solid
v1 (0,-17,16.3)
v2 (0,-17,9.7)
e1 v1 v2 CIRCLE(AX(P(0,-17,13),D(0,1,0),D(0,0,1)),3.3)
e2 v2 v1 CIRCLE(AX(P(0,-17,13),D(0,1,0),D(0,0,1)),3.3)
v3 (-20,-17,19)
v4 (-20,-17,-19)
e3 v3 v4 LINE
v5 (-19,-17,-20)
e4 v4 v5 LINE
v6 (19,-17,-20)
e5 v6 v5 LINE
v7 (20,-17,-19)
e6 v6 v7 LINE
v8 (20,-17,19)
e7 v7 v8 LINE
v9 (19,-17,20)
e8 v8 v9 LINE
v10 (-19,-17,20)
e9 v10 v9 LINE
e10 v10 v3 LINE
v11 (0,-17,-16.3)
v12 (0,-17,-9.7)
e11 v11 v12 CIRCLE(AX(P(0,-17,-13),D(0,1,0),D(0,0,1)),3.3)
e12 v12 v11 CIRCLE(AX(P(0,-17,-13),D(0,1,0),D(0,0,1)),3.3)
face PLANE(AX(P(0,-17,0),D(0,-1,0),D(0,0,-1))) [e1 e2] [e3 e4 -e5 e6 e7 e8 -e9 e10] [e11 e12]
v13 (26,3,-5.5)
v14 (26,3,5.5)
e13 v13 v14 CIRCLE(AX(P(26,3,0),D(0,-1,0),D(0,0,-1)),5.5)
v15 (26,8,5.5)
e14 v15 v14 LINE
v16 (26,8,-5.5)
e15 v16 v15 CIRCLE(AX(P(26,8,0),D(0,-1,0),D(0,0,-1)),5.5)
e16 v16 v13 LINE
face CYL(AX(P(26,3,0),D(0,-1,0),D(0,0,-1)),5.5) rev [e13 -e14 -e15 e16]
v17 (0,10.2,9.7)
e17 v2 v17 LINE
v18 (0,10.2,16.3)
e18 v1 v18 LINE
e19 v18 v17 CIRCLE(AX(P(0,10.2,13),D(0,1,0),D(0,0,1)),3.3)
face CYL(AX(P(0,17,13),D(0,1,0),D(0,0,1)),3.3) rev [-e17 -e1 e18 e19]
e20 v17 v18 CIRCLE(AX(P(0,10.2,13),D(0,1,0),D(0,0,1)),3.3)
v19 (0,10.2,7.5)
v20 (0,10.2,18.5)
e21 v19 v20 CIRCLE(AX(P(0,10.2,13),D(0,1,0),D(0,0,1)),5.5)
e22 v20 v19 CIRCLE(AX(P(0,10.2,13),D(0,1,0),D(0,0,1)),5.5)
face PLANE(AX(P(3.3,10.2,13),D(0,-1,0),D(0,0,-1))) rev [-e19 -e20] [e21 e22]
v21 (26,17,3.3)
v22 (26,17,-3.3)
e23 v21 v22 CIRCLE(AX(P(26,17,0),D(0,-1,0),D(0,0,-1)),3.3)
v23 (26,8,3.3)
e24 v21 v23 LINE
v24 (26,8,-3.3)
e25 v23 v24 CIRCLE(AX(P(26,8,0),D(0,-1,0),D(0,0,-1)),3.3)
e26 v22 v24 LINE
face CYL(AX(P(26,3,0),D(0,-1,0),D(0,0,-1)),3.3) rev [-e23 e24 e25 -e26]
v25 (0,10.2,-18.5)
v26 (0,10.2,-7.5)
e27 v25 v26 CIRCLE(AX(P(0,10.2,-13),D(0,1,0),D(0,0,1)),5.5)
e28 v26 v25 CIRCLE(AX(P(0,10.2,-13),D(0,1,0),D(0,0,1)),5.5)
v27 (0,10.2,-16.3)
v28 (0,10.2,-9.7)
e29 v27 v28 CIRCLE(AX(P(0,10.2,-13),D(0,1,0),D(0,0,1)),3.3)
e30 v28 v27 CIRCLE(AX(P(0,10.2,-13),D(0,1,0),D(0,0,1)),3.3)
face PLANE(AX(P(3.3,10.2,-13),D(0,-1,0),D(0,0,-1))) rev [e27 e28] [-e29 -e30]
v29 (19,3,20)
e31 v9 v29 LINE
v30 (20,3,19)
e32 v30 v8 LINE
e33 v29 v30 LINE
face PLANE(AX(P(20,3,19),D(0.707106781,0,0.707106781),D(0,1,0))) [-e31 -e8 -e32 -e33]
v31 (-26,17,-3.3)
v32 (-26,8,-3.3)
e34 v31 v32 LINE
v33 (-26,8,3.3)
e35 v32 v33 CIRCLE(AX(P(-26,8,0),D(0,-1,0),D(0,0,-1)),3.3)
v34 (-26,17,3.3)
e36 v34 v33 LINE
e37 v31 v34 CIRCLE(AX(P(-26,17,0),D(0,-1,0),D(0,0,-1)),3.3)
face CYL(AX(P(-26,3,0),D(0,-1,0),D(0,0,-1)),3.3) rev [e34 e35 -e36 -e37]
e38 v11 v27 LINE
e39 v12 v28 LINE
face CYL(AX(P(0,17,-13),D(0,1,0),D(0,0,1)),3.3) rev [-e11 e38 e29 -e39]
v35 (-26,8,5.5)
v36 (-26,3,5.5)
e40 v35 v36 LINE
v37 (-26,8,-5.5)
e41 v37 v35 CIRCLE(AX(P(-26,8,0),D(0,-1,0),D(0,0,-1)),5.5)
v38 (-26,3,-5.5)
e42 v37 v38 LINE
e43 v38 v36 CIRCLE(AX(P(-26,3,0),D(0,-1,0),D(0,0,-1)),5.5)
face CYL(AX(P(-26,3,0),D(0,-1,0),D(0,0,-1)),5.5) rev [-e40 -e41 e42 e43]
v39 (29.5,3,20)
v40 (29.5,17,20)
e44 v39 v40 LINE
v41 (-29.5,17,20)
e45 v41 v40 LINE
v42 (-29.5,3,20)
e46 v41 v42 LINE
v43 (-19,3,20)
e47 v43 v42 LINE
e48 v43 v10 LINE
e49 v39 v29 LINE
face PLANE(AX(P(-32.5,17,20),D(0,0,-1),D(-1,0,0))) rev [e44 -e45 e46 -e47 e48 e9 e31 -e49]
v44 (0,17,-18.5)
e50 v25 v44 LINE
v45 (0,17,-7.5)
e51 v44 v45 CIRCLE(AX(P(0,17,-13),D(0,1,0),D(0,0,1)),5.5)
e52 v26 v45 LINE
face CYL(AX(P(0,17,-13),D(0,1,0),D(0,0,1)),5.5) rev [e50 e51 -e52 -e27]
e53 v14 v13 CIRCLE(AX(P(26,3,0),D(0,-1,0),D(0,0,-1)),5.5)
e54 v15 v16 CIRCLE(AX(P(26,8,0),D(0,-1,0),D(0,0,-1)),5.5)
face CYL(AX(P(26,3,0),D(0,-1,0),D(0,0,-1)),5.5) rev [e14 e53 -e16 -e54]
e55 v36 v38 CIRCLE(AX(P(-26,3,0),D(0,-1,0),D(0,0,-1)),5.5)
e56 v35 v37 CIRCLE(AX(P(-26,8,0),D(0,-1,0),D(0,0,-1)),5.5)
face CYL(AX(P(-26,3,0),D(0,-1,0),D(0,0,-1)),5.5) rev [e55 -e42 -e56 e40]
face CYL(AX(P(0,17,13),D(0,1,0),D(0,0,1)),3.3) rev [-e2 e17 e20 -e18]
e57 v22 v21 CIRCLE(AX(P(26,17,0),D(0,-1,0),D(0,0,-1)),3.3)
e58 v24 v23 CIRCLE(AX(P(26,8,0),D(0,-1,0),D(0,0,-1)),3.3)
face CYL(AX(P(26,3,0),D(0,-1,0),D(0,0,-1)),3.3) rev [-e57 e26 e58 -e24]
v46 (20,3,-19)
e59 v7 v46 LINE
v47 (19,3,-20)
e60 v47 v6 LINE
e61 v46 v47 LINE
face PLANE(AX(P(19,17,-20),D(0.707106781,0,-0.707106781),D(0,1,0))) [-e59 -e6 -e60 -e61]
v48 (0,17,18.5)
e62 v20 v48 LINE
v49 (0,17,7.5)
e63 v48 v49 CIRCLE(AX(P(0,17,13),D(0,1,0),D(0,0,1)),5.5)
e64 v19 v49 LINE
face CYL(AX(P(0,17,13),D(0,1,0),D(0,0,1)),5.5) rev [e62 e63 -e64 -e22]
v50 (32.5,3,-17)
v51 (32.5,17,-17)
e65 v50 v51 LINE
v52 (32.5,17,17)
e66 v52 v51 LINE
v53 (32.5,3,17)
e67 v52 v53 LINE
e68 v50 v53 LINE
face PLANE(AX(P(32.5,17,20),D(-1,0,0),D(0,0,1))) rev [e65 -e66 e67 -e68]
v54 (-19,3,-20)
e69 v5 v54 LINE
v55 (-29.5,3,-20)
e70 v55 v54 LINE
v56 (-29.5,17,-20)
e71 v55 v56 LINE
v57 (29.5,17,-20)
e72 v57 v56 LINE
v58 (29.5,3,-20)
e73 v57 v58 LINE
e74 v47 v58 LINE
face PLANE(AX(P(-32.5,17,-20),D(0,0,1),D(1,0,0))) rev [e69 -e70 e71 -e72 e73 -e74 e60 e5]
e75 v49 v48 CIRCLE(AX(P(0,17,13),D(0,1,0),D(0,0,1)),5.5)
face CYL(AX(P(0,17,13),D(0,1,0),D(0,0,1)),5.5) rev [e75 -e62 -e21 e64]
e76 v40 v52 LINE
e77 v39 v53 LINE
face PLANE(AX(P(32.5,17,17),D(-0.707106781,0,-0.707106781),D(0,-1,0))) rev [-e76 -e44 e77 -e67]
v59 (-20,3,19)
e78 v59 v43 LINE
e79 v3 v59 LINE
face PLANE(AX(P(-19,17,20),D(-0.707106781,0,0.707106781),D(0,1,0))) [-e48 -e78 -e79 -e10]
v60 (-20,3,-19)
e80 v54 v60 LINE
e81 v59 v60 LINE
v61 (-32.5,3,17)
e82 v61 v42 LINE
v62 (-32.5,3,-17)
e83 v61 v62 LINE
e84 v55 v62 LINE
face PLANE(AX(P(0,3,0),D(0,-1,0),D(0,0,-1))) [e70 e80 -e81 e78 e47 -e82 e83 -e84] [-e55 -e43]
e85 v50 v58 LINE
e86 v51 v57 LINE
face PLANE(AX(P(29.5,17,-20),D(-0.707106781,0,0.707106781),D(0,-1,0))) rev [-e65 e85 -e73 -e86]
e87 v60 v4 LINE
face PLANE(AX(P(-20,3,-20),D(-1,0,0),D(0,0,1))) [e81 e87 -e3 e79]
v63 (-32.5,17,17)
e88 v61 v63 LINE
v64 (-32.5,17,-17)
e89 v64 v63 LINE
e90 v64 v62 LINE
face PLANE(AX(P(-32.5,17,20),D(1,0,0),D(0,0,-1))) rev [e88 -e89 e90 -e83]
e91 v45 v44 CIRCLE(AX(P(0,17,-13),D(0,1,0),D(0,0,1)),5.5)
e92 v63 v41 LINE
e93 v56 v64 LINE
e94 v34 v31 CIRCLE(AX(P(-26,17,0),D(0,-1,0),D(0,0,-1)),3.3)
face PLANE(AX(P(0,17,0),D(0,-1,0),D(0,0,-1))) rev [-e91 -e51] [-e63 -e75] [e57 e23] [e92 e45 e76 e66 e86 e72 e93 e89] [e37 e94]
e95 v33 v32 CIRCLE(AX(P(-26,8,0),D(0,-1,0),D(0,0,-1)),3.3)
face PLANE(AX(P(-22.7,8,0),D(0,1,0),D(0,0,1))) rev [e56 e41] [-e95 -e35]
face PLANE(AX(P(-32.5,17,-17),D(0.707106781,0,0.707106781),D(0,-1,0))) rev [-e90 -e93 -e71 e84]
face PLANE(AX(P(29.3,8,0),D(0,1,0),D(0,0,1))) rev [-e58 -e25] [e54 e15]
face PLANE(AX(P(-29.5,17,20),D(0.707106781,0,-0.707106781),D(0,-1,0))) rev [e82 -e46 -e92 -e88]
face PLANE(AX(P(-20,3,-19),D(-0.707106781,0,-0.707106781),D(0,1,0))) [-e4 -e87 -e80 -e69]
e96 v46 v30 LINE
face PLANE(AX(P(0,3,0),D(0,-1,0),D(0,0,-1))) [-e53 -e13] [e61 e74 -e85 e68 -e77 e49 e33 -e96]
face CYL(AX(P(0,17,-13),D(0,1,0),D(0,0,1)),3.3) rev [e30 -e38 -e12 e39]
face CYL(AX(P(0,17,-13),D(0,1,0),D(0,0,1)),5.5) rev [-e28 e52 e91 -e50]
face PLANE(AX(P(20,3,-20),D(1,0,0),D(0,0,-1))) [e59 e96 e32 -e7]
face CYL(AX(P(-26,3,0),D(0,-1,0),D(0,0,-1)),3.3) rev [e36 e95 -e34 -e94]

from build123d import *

# Parameters (mm, degrees)
SKETCH_1_W                  = 65
SKETCH_1_H                  = 40
EXTRUDE_1_DEPTH             = 17
HOLE_WIZARD_2_D             = 6.6
HOLE_WIZARD_2_CBORE_D       = 11
HOLE_WIZARD_2_CBORE_DEPTH   = 6.8
CHAMFER_1_SIZE              = 3
SKETCH_6_OUTSIDE_W          = 83.71
SKETCH_6_OUTSIDE_H          = 58.71
SKETCH_6_OUTSIDE_W_2        = 40
SKETCH_6_OUTSIDE_H_2        = 40
CUT_EXTRUDE_1_DEPTH         = 20
HOLE_WIZARD_2_2_D           = 6.6
HOLE_WIZARD_2_2_CBORE_D     = 11
HOLE_WIZARD_2_2_CBORE_DEPTH = 5
CHAMFER_2_SIZE              = 1


with BuildPart() as part:
    # 草图1 → 凸台-拉伸1 (new, symmetric)
    with BuildSketch(Plane(origin=(0, 0, 0), x_dir=(1, 0, 0), z_dir=(0, 1, 0))):
        Rectangle(SKETCH_1_W, SKETCH_1_H)
    extrude(amount=EXTRUDE_1_DEPTH, both=True)

    # Hole Wizard 2 (through all)
    with Locations(Plane(origin=(0, 17, 0), x_dir=(1, 0, 0), z_dir=(0, 1, 0))):
        with Locations((0, -13), (0, 13)):
            CounterBoreHole(HOLE_WIZARD_2_D / 2, HOLE_WIZARD_2_CBORE_D / 2, HOLE_WIZARD_2_CBORE_DEPTH)

    # 倒角1
    chamfer_1_edges = [part.edges().sort_by_distance(p)[0] for p in [
        (32.5, 0, 20),
        (-32.5, 0, 20),
        (-32.5, 0, -20),
        (32.5, 0, -20),
    ]]
    chamfer(chamfer_1_edges, length=CHAMFER_1_SIZE)

    # 草图6 outside → 切除-拉伸1 (cut)
    with BuildSketch(Plane.XZ.offset(17)):
        Rectangle(SKETCH_6_OUTSIDE_W, SKETCH_6_OUTSIDE_H)
        Rectangle(SKETCH_6_OUTSIDE_W_2, SKETCH_6_OUTSIDE_H_2, mode=Mode.SUBTRACT)
    extrude(amount=-CUT_EXTRUDE_1_DEPTH, mode=Mode.SUBTRACT)

    # Hole Wizard 2 2 (through all)
    with Locations(Plane.XZ.offset(-3)):
        with Locations((26, 0), (-26, 0)):
            CounterBoreHole(HOLE_WIZARD_2_2_D / 2, HOLE_WIZARD_2_2_CBORE_D / 2, HOLE_WIZARD_2_2_CBORE_DEPTH)

    # 倒角2
    chamfer_2_edges = [part.edges().sort_by_distance(p)[0] for p in [
        (-20, -7, 20),
        (20, -7, 20),
        (20, -7, -20),
        (-20, -7, -20),
    ]]
    chamfer(chamfer_2_edges, length=CHAMFER_2_SIZE)


solid = part.part
